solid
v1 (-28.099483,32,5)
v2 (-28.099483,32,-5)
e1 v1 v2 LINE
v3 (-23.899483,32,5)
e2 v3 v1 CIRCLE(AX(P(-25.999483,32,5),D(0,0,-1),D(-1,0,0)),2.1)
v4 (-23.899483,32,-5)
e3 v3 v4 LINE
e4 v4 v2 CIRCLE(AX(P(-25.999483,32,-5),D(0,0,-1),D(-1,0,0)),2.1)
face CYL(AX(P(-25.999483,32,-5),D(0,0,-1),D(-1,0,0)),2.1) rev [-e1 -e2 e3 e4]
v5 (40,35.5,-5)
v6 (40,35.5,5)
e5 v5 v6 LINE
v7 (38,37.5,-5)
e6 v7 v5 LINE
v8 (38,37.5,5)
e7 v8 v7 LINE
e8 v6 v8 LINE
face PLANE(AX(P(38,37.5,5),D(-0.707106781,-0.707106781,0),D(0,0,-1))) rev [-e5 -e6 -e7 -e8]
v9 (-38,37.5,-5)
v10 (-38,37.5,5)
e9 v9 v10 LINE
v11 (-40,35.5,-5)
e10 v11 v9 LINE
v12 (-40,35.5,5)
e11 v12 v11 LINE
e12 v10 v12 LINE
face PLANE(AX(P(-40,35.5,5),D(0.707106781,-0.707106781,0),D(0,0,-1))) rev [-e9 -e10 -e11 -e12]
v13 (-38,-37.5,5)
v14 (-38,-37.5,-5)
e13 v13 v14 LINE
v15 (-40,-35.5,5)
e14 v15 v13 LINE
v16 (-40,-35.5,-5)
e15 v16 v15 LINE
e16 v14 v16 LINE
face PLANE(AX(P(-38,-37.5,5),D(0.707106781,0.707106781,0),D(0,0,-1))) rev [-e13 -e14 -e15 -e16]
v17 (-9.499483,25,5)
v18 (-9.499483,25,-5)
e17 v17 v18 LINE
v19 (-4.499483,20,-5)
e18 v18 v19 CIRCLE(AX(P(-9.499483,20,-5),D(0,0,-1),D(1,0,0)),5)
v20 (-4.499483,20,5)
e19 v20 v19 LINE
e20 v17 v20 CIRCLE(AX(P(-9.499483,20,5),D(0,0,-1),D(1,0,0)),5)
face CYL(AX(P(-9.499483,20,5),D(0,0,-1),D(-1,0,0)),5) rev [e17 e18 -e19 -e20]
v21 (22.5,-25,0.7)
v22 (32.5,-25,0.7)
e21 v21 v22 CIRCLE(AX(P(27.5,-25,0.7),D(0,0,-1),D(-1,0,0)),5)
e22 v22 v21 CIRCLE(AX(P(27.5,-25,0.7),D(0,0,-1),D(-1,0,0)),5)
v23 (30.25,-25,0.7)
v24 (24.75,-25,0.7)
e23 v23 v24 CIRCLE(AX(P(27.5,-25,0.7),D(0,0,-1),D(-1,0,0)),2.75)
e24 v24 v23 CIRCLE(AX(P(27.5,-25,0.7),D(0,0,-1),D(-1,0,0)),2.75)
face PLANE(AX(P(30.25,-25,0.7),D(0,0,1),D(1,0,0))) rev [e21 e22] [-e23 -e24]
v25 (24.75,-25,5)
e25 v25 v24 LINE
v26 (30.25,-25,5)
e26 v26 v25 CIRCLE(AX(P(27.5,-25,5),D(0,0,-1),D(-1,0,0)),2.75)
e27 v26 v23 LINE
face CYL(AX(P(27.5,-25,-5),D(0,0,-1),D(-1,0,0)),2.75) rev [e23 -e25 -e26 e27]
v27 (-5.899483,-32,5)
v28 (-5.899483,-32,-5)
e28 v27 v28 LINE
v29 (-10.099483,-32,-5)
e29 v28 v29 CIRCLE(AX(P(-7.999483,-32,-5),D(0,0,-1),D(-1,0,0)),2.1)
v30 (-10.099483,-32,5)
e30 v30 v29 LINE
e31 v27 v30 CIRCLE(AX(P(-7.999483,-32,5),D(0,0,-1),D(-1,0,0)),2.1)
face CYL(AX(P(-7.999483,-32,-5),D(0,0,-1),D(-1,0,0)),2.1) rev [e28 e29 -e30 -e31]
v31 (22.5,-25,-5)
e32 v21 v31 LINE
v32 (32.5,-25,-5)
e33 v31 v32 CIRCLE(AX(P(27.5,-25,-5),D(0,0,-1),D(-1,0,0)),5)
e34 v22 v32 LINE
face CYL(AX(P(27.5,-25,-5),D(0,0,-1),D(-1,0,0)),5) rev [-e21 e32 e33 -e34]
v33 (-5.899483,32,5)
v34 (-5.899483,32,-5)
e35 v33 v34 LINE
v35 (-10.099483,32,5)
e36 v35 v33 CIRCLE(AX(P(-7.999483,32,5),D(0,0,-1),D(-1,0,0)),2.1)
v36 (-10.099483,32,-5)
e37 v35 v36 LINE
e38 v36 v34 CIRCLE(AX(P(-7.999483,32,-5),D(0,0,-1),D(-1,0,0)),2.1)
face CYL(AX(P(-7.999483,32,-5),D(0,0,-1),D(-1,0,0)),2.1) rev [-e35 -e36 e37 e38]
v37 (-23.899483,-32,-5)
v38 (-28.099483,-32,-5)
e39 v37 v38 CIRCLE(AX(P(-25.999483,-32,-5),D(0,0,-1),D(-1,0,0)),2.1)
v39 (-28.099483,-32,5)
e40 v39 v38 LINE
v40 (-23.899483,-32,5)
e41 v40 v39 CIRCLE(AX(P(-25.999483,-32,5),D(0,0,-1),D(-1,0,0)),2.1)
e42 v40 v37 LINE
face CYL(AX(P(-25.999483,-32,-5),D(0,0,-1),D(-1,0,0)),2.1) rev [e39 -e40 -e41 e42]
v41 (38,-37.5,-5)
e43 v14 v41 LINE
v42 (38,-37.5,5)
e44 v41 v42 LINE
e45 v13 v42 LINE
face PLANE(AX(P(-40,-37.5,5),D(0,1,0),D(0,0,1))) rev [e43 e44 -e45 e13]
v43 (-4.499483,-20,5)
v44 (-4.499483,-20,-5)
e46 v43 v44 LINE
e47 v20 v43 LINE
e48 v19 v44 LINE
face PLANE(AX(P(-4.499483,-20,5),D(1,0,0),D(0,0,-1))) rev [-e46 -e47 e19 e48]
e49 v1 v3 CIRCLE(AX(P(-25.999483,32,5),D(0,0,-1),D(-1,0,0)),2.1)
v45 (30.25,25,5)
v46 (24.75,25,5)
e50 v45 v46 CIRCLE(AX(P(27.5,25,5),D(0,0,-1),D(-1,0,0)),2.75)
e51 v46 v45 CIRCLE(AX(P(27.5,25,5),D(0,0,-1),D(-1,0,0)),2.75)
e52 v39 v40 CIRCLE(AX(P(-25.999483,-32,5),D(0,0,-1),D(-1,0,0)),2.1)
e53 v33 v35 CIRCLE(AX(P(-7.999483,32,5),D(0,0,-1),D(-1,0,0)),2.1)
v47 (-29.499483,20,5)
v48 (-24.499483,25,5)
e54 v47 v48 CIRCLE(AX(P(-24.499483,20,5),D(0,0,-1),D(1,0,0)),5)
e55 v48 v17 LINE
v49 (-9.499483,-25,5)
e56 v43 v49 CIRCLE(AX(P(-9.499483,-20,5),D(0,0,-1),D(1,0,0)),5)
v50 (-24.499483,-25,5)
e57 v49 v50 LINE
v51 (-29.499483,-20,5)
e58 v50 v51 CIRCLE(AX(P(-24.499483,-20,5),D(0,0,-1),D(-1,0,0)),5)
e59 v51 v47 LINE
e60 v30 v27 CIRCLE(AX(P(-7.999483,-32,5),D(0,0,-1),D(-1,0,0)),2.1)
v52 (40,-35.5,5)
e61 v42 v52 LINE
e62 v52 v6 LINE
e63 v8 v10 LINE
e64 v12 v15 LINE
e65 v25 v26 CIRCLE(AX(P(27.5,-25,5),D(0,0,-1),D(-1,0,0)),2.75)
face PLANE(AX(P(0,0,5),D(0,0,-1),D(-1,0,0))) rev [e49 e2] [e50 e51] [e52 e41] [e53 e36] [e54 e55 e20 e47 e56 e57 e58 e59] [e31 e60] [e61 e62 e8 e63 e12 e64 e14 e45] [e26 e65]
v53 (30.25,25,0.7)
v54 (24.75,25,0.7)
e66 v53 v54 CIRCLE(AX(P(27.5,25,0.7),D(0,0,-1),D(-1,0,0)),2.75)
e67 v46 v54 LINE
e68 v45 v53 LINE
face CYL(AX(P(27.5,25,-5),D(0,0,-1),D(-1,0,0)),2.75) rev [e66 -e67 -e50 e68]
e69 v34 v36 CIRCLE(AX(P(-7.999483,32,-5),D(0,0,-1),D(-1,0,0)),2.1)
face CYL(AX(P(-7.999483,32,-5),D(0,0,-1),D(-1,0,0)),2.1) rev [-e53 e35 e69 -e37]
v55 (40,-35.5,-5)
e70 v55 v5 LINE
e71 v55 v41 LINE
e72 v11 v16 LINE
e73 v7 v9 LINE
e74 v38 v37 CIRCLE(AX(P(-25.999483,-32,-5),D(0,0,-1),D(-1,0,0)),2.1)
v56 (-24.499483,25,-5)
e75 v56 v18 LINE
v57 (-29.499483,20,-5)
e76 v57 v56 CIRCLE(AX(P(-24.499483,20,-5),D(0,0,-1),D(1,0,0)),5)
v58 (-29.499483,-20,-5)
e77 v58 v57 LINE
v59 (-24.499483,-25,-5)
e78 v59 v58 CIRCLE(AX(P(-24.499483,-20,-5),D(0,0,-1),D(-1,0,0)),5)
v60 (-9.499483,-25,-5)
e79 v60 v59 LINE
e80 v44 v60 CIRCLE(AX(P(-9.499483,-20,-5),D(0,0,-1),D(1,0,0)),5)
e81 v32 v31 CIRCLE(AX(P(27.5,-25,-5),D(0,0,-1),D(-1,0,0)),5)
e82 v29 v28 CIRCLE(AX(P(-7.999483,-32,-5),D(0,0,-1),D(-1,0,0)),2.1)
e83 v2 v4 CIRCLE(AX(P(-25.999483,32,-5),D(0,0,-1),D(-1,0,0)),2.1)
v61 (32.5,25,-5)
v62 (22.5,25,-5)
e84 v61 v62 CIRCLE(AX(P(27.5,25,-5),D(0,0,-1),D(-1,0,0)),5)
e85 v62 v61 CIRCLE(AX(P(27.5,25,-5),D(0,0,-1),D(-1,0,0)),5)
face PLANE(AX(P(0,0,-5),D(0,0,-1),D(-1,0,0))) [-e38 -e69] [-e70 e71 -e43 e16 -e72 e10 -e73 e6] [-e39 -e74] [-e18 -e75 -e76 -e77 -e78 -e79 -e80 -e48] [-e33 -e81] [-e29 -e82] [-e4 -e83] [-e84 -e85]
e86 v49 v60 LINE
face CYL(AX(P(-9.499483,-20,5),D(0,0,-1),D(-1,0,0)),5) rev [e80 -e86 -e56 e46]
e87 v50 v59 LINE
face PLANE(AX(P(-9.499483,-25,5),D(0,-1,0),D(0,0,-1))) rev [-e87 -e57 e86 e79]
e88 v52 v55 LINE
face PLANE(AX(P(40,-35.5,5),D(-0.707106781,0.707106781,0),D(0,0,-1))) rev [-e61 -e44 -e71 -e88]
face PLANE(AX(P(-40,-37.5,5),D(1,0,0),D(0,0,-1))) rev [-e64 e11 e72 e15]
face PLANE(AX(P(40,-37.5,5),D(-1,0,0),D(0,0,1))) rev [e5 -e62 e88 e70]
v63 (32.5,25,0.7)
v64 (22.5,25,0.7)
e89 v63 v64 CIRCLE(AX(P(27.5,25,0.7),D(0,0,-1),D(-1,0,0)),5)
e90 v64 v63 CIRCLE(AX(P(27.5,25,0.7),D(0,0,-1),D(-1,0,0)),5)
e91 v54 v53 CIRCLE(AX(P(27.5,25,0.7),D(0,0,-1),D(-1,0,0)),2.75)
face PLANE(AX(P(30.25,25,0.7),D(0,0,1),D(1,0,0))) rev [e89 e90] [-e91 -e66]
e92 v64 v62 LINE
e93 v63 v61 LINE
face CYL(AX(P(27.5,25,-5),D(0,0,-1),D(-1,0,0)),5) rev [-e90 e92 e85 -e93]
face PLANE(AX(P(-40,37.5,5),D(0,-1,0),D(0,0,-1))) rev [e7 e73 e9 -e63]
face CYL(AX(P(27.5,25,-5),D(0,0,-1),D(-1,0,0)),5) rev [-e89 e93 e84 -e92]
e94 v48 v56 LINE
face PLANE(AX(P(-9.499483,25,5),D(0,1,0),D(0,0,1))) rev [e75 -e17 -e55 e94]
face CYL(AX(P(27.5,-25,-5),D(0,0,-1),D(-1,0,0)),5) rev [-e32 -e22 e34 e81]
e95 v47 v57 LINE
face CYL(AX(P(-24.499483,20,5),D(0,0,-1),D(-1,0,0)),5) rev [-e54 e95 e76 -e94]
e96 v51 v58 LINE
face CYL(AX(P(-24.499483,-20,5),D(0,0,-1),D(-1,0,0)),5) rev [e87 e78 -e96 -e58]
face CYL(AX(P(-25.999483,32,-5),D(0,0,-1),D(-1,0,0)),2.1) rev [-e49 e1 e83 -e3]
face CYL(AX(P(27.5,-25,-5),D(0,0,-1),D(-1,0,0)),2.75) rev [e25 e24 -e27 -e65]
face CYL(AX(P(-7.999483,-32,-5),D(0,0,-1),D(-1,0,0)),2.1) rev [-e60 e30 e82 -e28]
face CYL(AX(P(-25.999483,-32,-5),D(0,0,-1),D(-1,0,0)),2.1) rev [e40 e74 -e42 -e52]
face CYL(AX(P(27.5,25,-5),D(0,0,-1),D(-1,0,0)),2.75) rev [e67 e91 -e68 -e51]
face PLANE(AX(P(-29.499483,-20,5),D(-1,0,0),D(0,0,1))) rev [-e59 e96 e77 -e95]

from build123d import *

# Parameters (mm, degrees)
SKETCH_1_W                   = 80
SKETCH_1_H                   = 75
EXTRUDE_1_DEPTH              = 5
CHAMFER_1_SIZE               = 2
HOLE_WIZARD_M5_1_D           = 5.5
HOLE_WIZARD_M5_1_CBORE_D     = 10
HOLE_WIZARD_M5_1_CBORE_DEPTH = 5.7
HOLE_WIZARD_M5_1_2_D         = 4.2
HOLE_WIZARD_M5_1_2_DEPTH     = 12.4
HOLE_WIZARD_M5_1_2_TIP       = 1.2618073
CUT_EXTRUDE_1_DEPTH          = 56.733742024


with BuildPart() as part:
    # 草图1 → 凸台-拉伸1 (new, symmetric)
    with BuildSketch(Plane.XY):
        Rectangle(SKETCH_1_W, SKETCH_1_H)
    extrude(amount=EXTRUDE_1_DEPTH, both=True)

    # 倒角1
    chamfer_1_edges = [part.edges().sort_by_distance(p)[0] for p in [
        (40, -37.5, 0),
        (-40, -37.5, 0),
        (-40, 37.5, 0),
        (40, 37.5, 0),
    ]]
    chamfer(chamfer_1_edges, length=CHAMFER_1_SIZE)

    # Hole Wizard M5 _1 (through all)
    with Locations(Plane(origin=(0, 0, -5), x_dir=(-1, 0, 0), z_dir=(0, 0, -1))):
        with Locations((-27.5, 25), (-27.5, -25)):
            CounterBoreHole(HOLE_WIZARD_M5_1_D / 2, HOLE_WIZARD_M5_1_CBORE_D / 2, HOLE_WIZARD_M5_1_CBORE_DEPTH)

    # Hole Wizard M5 _1 2
    with Locations(Plane(origin=(0, 0, -5), x_dir=(-1, 0, 0), z_dir=(0, 0, -1))):
        with Locations((7.999483419, 32), (25.999483419, 32), (7.999483419, -32), (25.999483419, -32)):
            Hole(HOLE_WIZARD_M5_1_2_D / 2, depth=HOLE_WIZARD_M5_1_2_DEPTH)
            with Locations((0, 0, -(HOLE_WIZARD_M5_1_2_DEPTH + HOLE_WIZARD_M5_1_2_TIP / 2))):  # 118° drill point
                Cone(0, HOLE_WIZARD_M5_1_2_D / 2, HOLE_WIZARD_M5_1_2_TIP, mode=Mode.SUBTRACT)

    # 草图8 → 切除-拉伸1 (cut, through all)
    with BuildSketch(Plane(origin=(0, 0, -5), x_dir=(-1, 0, 0), z_dir=(0, 0, -1))):
        with BuildLine():
            Line((9.499483419, -25), (24.499483419, -25))
            ThreePointArc((24.499483419, -25), (28.035017325, -23.535533906), (29.499483419, -20))
            Line((29.499483419, -20), (29.499483419, 20))
            ThreePointArc((29.499483419, 20), (28.035017325, 23.535533906), (24.499483419, 25))
            Line((24.499483419, 25), (9.499483419, 25))
            ThreePointArc((9.499483419, 25), (5.963949513, 23.535533906), (4.499483419, 20))
            Line((4.499483419, 20), (4.499483419, -20))
            ThreePointArc((4.499483419, -20), (5.963949513, -23.535533906), (9.499483419, -25))
        make_face()
    extrude(amount=-CUT_EXTRUDE_1_DEPTH, mode=Mode.SUBTRACT)


solid = part.part
